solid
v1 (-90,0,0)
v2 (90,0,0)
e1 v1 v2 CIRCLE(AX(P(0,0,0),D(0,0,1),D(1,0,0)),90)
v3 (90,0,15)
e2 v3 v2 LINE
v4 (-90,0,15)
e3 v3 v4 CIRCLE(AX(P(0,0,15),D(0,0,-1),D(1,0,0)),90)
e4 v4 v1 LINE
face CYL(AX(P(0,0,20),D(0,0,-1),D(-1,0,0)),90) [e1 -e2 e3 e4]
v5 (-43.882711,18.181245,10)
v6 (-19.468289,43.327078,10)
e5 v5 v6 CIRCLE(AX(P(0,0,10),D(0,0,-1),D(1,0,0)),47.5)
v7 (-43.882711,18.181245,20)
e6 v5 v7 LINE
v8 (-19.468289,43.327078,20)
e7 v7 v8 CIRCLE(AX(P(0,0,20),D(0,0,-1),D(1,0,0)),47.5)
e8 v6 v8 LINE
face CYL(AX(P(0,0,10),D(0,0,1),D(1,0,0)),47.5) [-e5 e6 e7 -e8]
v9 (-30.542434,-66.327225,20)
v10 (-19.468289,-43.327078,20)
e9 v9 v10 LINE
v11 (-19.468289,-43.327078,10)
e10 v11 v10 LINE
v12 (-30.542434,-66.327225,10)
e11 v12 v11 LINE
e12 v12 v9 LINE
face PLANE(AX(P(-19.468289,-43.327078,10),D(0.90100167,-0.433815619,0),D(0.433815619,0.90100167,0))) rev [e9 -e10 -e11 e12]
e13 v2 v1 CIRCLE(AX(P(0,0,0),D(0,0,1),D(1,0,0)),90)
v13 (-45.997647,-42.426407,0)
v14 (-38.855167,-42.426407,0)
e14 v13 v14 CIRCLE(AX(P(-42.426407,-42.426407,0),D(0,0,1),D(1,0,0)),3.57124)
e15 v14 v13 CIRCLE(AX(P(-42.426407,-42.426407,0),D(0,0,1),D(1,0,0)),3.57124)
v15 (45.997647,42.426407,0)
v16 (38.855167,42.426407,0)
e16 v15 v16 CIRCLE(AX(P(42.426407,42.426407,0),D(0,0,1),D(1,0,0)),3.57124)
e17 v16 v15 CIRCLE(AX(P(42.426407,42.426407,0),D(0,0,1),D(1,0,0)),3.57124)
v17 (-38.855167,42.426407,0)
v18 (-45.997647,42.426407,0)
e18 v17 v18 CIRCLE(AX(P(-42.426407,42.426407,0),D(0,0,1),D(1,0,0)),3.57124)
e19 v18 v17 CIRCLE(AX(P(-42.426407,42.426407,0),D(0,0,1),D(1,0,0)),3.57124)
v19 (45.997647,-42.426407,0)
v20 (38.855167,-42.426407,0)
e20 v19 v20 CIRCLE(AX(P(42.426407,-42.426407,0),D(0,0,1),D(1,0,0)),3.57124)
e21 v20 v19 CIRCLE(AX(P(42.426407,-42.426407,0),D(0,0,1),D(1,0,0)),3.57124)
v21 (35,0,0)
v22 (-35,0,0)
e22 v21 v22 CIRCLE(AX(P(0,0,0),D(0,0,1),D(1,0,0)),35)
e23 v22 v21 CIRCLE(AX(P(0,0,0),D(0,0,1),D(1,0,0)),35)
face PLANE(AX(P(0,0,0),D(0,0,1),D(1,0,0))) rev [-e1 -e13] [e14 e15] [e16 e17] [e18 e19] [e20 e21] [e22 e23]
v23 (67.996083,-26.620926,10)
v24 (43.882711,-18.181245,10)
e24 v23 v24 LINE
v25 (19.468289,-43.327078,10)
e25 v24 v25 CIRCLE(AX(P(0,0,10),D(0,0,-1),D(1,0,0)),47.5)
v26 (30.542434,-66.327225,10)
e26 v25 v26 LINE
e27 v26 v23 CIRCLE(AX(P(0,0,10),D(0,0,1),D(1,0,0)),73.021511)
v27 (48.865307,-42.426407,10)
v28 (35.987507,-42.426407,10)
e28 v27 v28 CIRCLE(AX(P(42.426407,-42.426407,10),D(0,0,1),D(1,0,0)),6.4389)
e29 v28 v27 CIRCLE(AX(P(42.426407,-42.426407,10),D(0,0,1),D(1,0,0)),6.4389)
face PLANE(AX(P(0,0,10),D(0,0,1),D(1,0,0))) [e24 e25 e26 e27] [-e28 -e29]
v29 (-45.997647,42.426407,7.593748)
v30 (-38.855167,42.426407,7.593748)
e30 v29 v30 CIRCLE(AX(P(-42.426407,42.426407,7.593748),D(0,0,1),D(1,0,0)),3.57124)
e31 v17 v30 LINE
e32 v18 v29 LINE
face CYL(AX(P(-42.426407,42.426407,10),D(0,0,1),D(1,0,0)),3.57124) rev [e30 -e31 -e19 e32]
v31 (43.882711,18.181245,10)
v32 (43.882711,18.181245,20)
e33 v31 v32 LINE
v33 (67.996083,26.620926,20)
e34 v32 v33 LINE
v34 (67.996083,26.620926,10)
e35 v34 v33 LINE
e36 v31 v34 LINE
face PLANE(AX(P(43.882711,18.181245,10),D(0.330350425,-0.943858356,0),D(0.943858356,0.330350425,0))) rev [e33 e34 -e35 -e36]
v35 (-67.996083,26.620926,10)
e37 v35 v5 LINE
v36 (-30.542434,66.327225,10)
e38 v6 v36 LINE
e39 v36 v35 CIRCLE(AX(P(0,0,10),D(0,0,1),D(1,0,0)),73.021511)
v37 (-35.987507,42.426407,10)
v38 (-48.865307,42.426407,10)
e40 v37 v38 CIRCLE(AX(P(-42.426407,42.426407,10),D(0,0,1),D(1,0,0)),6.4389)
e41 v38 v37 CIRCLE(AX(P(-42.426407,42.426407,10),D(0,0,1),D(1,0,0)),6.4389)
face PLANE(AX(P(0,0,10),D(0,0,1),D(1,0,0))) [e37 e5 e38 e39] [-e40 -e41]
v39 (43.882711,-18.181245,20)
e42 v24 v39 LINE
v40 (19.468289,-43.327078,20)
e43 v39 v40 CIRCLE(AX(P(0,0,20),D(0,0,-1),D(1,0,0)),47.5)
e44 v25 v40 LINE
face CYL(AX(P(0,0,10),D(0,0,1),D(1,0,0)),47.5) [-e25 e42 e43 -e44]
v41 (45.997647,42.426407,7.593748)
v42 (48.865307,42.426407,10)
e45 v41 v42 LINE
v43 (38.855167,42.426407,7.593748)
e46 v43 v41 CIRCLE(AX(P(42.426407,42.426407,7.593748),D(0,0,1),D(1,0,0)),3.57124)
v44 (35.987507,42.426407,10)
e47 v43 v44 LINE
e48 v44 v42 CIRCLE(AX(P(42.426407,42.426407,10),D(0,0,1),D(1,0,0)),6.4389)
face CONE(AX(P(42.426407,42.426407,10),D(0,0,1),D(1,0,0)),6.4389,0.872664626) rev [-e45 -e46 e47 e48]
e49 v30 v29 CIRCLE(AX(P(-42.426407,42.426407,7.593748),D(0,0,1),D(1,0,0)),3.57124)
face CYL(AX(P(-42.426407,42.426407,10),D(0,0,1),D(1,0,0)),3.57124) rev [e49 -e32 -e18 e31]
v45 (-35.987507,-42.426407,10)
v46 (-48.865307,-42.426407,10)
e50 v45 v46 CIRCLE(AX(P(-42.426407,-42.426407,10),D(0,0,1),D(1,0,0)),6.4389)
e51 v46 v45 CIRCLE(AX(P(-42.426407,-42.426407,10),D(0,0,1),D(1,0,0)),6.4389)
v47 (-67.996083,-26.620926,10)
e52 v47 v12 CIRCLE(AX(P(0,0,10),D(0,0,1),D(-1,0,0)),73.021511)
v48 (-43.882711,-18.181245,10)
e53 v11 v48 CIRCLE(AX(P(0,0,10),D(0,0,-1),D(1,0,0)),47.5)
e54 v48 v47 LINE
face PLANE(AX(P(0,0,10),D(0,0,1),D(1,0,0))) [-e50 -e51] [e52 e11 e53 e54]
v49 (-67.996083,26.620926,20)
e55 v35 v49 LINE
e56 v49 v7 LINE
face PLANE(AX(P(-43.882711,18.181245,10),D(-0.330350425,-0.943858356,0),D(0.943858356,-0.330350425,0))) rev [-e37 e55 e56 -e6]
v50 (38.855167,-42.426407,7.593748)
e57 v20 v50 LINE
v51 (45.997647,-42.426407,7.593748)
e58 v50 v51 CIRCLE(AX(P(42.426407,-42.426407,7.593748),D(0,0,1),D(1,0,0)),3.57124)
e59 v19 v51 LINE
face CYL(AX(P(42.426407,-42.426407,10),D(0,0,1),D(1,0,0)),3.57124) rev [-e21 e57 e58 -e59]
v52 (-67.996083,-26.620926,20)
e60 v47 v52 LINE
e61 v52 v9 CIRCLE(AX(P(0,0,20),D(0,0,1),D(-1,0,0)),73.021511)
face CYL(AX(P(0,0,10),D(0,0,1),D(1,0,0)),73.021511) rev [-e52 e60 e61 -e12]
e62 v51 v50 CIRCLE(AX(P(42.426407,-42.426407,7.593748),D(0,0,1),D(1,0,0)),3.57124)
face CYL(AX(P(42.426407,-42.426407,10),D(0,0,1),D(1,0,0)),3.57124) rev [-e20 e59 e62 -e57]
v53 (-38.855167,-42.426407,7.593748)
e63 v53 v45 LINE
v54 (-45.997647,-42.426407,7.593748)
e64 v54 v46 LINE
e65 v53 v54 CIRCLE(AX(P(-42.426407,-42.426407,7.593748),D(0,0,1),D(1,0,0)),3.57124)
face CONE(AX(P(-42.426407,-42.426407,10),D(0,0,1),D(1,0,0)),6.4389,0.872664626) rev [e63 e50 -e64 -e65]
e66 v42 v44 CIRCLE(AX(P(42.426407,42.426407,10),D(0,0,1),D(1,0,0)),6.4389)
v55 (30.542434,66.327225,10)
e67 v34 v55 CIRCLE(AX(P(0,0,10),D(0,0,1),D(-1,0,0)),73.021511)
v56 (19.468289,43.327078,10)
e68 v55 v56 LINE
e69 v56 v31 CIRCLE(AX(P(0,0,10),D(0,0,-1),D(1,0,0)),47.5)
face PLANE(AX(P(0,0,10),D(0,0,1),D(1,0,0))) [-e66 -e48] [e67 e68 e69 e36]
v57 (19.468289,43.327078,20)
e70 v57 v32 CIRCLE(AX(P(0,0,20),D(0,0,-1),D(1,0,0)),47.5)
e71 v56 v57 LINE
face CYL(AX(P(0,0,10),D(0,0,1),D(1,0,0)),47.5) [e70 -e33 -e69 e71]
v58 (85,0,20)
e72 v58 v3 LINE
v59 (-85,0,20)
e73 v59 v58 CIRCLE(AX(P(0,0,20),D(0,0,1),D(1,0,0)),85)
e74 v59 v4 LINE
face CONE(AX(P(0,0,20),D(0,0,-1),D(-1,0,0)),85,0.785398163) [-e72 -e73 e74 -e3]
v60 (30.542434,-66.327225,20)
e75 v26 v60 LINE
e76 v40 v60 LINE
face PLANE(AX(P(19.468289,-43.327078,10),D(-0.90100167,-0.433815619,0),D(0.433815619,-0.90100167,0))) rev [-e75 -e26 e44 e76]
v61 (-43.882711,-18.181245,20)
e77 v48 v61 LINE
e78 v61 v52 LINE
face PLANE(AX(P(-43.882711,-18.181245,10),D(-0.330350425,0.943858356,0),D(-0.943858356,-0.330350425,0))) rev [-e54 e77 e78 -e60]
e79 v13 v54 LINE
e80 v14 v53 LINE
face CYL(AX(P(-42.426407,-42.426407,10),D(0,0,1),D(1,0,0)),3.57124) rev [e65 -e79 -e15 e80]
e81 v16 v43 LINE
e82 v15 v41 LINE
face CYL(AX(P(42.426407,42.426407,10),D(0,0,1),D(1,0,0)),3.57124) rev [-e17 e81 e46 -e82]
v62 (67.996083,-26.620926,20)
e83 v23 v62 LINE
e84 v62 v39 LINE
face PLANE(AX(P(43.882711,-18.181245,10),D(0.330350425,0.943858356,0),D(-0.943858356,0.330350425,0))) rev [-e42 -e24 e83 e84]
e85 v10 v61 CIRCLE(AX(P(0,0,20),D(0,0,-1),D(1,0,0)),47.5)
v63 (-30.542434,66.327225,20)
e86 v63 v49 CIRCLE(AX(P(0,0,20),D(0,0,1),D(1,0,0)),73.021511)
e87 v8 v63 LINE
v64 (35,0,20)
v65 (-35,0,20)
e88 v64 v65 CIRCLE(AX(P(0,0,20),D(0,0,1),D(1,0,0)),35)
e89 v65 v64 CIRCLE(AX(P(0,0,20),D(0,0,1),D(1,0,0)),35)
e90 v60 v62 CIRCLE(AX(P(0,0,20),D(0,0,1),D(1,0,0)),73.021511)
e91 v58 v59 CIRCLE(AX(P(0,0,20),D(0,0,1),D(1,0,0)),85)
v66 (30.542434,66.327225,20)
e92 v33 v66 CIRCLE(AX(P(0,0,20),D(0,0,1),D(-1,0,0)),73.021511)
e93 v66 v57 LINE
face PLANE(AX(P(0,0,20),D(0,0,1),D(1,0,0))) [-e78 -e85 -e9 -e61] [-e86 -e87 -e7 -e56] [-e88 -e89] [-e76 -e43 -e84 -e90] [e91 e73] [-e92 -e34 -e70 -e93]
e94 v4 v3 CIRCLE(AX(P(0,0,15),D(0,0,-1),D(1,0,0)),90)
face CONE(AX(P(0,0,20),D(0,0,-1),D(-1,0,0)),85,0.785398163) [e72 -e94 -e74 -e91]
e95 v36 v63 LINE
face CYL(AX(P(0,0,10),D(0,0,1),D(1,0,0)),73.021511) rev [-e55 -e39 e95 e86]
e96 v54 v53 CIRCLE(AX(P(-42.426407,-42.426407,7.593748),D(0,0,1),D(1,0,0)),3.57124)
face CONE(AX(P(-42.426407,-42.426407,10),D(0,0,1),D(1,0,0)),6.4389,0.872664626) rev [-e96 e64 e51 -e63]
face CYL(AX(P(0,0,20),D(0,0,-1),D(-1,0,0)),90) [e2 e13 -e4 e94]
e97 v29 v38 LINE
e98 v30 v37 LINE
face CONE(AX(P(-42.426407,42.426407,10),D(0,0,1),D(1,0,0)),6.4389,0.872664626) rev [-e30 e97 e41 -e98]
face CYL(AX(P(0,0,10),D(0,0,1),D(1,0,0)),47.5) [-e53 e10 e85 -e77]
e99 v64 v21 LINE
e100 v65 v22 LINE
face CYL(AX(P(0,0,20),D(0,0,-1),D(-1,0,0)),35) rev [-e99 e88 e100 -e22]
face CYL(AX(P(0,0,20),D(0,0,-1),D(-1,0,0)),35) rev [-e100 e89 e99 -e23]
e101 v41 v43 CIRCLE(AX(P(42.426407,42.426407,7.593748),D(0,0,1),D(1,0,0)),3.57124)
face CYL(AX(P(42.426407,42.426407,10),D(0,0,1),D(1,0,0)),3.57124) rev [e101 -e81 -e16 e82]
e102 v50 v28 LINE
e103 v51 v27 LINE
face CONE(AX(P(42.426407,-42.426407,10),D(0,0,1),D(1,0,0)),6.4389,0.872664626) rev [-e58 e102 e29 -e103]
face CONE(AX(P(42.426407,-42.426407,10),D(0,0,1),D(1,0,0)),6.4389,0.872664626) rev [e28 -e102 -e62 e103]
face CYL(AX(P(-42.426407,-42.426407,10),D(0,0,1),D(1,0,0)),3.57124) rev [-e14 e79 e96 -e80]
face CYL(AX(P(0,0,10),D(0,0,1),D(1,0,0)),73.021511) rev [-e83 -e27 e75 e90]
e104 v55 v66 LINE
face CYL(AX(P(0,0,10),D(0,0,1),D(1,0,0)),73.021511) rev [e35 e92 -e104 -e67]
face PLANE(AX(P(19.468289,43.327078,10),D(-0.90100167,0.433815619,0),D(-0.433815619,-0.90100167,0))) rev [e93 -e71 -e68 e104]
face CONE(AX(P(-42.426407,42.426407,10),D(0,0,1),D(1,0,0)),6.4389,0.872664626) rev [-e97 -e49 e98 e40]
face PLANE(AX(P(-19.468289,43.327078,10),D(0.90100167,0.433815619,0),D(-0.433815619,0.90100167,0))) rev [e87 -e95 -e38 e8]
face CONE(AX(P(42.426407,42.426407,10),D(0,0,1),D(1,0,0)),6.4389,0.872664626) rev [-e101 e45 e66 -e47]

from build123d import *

# Parameters (mm, degrees)
SKETCH1_R                                           = 90
SKETCH1_R_2                                         = 35
BOSS_EXTRUDE1_DEPTH                                 = 20
CUT_EXTRUDE1_DEPTH                                  = 10
CHAMFER1_SIZE                                       = 5
CSK_FOR_1_4_FLAT_HEAD_MACHINE_SCREW_100_D           = 7.14248
CSK_FOR_1_4_FLAT_HEAD_MACHINE_SCREW_100_CSINK_D     = 12.8778
CSK_FOR_1_4_FLAT_HEAD_MACHINE_SCREW_100_CSINK_ANGLE = 100
MIRROR2_COPY_1_D                                    = 7.14248
MIRROR2_COPY_1_CSINK_D                              = 12.8778
MIRROR2_COPY_1_CSINK_ANGLE                          = 100


with BuildPart() as part:
    # Sketch1 → Boss-Extrude1 (new body)
    with BuildSketch(Plane.XY):
        Circle(SKETCH1_R)
        Circle(SKETCH1_R_2, mode=Mode.SUBTRACT)
    extrude(amount=BOSS_EXTRUDE1_DEPTH)

    # Sketch2 → Cut-Extrude1 (cut)
    with BuildSketch(Plane.XY.offset(20)):
        with BuildLine():
            Line((-19.468288874, 43.327078465), (-30.54243357, 66.327225141))
            ThreePointArc((-30.54243357, 66.327225141), (-53.118804443, 50.105225854), (-67.996083401, 26.620925706))
            Line((-67.996083401, 26.620925706), (-43.882710923, 18.181245339))
            ThreePointArc((-43.882710923, 18.181245339), (-34.079547015, 33.088283051), (-19.468288874, 43.327078465))
        make_face()
        with BuildLine():
            Line((43.882710923, 18.181245339), (67.996083401, 26.620925706))
            ThreePointArc((67.996083401, 26.620925706), (53.118804443, 50.105225854), (30.54243357, 66.327225141))
            Line((30.54243357, 66.327225141), (19.468288874, 43.327078465))
            ThreePointArc((19.468288874, 43.327078465), (34.079547015, 33.088283051), (43.882710923, 18.181245339))
        make_face()
        with BuildLine():
            Line((19.468288874, -43.327078465), (30.54243357, -66.327225141))
            ThreePointArc((30.54243357, -66.327225141), (53.118804443, -50.105225854), (67.996083401, -26.620925706))
            Line((67.996083401, -26.620925706), (43.882710923, -18.181245339))
            ThreePointArc((43.882710923, -18.181245339), (34.079547015, -33.088283051), (19.468288874, -43.327078465))
        make_face()
        with BuildLine():
            Line((-43.882710923, -18.181245339), (-67.996083401, -26.620925706))
            ThreePointArc((-67.996083401, -26.620925706), (-53.118804443, -50.105225854), (-30.54243357, -66.327225141))
            Line((-30.54243357, -66.327225141), (-19.468288874, -43.327078465))
            ThreePointArc((-19.468288874, -43.327078465), (-34.079547015, -33.088283051), (-43.882710923, -18.181245339))
        make_face()
    extrude(amount=-CUT_EXTRUDE1_DEPTH, mode=Mode.SUBTRACT)

    # Chamfer1
    chamfer1_edges = [part.edges().sort_by_distance(p)[0] for p in [
        (-90, 0, 20),
    ]]
    chamfer(chamfer1_edges, length=CHAMFER1_SIZE)

    # CSK for 1/4 Flat Head Machine Screw (100)1 (through all)
    with Locations(Plane.XY.offset(10)):
        with Locations((-42.426406871, 42.426406871)):
            csk_for_1_4_flat_head_machine_screw_100 = CounterSinkHole(CSK_FOR_1_4_FLAT_HEAD_MACHINE_SCREW_100_D / 2, CSK_FOR_1_4_FLAT_HEAD_MACHINE_SCREW_100_CSINK_D / 2, counter_sink_angle=CSK_FOR_1_4_FLAT_HEAD_MACHINE_SCREW_100_CSINK_ANGLE)

    # Mirror1: CSK for 1/4 Flat Head Machine Screw (100)1 across plane
    add(csk_for_1_4_flat_head_machine_screw_100.mirror(Plane(origin=(0, 0, 0), x_dir=(0, 0, 1), z_dir=(1, 0, 0))), mode=Mode.SUBTRACT)

    # Mirror2: CSK for 1/4 Flat Head Machine Screw (100)1 across plane
    add(csk_for_1_4_flat_head_machine_screw_100.mirror(Plane.ZX), mode=Mode.SUBTRACT)

    # Mirror2 copy 1 (through all)
    with Locations(Plane(origin=(0, 0, 10), x_dir=(-1, 0, 0), z_dir=(0, 0, 1))):
        with Locations((-42.426406871, 42.426406871)):
            CounterSinkHole(MIRROR2_COPY_1_D / 2, MIRROR2_COPY_1_CSINK_D / 2, counter_sink_angle=MIRROR2_COPY_1_CSINK_ANGLE)


solid = part.part
